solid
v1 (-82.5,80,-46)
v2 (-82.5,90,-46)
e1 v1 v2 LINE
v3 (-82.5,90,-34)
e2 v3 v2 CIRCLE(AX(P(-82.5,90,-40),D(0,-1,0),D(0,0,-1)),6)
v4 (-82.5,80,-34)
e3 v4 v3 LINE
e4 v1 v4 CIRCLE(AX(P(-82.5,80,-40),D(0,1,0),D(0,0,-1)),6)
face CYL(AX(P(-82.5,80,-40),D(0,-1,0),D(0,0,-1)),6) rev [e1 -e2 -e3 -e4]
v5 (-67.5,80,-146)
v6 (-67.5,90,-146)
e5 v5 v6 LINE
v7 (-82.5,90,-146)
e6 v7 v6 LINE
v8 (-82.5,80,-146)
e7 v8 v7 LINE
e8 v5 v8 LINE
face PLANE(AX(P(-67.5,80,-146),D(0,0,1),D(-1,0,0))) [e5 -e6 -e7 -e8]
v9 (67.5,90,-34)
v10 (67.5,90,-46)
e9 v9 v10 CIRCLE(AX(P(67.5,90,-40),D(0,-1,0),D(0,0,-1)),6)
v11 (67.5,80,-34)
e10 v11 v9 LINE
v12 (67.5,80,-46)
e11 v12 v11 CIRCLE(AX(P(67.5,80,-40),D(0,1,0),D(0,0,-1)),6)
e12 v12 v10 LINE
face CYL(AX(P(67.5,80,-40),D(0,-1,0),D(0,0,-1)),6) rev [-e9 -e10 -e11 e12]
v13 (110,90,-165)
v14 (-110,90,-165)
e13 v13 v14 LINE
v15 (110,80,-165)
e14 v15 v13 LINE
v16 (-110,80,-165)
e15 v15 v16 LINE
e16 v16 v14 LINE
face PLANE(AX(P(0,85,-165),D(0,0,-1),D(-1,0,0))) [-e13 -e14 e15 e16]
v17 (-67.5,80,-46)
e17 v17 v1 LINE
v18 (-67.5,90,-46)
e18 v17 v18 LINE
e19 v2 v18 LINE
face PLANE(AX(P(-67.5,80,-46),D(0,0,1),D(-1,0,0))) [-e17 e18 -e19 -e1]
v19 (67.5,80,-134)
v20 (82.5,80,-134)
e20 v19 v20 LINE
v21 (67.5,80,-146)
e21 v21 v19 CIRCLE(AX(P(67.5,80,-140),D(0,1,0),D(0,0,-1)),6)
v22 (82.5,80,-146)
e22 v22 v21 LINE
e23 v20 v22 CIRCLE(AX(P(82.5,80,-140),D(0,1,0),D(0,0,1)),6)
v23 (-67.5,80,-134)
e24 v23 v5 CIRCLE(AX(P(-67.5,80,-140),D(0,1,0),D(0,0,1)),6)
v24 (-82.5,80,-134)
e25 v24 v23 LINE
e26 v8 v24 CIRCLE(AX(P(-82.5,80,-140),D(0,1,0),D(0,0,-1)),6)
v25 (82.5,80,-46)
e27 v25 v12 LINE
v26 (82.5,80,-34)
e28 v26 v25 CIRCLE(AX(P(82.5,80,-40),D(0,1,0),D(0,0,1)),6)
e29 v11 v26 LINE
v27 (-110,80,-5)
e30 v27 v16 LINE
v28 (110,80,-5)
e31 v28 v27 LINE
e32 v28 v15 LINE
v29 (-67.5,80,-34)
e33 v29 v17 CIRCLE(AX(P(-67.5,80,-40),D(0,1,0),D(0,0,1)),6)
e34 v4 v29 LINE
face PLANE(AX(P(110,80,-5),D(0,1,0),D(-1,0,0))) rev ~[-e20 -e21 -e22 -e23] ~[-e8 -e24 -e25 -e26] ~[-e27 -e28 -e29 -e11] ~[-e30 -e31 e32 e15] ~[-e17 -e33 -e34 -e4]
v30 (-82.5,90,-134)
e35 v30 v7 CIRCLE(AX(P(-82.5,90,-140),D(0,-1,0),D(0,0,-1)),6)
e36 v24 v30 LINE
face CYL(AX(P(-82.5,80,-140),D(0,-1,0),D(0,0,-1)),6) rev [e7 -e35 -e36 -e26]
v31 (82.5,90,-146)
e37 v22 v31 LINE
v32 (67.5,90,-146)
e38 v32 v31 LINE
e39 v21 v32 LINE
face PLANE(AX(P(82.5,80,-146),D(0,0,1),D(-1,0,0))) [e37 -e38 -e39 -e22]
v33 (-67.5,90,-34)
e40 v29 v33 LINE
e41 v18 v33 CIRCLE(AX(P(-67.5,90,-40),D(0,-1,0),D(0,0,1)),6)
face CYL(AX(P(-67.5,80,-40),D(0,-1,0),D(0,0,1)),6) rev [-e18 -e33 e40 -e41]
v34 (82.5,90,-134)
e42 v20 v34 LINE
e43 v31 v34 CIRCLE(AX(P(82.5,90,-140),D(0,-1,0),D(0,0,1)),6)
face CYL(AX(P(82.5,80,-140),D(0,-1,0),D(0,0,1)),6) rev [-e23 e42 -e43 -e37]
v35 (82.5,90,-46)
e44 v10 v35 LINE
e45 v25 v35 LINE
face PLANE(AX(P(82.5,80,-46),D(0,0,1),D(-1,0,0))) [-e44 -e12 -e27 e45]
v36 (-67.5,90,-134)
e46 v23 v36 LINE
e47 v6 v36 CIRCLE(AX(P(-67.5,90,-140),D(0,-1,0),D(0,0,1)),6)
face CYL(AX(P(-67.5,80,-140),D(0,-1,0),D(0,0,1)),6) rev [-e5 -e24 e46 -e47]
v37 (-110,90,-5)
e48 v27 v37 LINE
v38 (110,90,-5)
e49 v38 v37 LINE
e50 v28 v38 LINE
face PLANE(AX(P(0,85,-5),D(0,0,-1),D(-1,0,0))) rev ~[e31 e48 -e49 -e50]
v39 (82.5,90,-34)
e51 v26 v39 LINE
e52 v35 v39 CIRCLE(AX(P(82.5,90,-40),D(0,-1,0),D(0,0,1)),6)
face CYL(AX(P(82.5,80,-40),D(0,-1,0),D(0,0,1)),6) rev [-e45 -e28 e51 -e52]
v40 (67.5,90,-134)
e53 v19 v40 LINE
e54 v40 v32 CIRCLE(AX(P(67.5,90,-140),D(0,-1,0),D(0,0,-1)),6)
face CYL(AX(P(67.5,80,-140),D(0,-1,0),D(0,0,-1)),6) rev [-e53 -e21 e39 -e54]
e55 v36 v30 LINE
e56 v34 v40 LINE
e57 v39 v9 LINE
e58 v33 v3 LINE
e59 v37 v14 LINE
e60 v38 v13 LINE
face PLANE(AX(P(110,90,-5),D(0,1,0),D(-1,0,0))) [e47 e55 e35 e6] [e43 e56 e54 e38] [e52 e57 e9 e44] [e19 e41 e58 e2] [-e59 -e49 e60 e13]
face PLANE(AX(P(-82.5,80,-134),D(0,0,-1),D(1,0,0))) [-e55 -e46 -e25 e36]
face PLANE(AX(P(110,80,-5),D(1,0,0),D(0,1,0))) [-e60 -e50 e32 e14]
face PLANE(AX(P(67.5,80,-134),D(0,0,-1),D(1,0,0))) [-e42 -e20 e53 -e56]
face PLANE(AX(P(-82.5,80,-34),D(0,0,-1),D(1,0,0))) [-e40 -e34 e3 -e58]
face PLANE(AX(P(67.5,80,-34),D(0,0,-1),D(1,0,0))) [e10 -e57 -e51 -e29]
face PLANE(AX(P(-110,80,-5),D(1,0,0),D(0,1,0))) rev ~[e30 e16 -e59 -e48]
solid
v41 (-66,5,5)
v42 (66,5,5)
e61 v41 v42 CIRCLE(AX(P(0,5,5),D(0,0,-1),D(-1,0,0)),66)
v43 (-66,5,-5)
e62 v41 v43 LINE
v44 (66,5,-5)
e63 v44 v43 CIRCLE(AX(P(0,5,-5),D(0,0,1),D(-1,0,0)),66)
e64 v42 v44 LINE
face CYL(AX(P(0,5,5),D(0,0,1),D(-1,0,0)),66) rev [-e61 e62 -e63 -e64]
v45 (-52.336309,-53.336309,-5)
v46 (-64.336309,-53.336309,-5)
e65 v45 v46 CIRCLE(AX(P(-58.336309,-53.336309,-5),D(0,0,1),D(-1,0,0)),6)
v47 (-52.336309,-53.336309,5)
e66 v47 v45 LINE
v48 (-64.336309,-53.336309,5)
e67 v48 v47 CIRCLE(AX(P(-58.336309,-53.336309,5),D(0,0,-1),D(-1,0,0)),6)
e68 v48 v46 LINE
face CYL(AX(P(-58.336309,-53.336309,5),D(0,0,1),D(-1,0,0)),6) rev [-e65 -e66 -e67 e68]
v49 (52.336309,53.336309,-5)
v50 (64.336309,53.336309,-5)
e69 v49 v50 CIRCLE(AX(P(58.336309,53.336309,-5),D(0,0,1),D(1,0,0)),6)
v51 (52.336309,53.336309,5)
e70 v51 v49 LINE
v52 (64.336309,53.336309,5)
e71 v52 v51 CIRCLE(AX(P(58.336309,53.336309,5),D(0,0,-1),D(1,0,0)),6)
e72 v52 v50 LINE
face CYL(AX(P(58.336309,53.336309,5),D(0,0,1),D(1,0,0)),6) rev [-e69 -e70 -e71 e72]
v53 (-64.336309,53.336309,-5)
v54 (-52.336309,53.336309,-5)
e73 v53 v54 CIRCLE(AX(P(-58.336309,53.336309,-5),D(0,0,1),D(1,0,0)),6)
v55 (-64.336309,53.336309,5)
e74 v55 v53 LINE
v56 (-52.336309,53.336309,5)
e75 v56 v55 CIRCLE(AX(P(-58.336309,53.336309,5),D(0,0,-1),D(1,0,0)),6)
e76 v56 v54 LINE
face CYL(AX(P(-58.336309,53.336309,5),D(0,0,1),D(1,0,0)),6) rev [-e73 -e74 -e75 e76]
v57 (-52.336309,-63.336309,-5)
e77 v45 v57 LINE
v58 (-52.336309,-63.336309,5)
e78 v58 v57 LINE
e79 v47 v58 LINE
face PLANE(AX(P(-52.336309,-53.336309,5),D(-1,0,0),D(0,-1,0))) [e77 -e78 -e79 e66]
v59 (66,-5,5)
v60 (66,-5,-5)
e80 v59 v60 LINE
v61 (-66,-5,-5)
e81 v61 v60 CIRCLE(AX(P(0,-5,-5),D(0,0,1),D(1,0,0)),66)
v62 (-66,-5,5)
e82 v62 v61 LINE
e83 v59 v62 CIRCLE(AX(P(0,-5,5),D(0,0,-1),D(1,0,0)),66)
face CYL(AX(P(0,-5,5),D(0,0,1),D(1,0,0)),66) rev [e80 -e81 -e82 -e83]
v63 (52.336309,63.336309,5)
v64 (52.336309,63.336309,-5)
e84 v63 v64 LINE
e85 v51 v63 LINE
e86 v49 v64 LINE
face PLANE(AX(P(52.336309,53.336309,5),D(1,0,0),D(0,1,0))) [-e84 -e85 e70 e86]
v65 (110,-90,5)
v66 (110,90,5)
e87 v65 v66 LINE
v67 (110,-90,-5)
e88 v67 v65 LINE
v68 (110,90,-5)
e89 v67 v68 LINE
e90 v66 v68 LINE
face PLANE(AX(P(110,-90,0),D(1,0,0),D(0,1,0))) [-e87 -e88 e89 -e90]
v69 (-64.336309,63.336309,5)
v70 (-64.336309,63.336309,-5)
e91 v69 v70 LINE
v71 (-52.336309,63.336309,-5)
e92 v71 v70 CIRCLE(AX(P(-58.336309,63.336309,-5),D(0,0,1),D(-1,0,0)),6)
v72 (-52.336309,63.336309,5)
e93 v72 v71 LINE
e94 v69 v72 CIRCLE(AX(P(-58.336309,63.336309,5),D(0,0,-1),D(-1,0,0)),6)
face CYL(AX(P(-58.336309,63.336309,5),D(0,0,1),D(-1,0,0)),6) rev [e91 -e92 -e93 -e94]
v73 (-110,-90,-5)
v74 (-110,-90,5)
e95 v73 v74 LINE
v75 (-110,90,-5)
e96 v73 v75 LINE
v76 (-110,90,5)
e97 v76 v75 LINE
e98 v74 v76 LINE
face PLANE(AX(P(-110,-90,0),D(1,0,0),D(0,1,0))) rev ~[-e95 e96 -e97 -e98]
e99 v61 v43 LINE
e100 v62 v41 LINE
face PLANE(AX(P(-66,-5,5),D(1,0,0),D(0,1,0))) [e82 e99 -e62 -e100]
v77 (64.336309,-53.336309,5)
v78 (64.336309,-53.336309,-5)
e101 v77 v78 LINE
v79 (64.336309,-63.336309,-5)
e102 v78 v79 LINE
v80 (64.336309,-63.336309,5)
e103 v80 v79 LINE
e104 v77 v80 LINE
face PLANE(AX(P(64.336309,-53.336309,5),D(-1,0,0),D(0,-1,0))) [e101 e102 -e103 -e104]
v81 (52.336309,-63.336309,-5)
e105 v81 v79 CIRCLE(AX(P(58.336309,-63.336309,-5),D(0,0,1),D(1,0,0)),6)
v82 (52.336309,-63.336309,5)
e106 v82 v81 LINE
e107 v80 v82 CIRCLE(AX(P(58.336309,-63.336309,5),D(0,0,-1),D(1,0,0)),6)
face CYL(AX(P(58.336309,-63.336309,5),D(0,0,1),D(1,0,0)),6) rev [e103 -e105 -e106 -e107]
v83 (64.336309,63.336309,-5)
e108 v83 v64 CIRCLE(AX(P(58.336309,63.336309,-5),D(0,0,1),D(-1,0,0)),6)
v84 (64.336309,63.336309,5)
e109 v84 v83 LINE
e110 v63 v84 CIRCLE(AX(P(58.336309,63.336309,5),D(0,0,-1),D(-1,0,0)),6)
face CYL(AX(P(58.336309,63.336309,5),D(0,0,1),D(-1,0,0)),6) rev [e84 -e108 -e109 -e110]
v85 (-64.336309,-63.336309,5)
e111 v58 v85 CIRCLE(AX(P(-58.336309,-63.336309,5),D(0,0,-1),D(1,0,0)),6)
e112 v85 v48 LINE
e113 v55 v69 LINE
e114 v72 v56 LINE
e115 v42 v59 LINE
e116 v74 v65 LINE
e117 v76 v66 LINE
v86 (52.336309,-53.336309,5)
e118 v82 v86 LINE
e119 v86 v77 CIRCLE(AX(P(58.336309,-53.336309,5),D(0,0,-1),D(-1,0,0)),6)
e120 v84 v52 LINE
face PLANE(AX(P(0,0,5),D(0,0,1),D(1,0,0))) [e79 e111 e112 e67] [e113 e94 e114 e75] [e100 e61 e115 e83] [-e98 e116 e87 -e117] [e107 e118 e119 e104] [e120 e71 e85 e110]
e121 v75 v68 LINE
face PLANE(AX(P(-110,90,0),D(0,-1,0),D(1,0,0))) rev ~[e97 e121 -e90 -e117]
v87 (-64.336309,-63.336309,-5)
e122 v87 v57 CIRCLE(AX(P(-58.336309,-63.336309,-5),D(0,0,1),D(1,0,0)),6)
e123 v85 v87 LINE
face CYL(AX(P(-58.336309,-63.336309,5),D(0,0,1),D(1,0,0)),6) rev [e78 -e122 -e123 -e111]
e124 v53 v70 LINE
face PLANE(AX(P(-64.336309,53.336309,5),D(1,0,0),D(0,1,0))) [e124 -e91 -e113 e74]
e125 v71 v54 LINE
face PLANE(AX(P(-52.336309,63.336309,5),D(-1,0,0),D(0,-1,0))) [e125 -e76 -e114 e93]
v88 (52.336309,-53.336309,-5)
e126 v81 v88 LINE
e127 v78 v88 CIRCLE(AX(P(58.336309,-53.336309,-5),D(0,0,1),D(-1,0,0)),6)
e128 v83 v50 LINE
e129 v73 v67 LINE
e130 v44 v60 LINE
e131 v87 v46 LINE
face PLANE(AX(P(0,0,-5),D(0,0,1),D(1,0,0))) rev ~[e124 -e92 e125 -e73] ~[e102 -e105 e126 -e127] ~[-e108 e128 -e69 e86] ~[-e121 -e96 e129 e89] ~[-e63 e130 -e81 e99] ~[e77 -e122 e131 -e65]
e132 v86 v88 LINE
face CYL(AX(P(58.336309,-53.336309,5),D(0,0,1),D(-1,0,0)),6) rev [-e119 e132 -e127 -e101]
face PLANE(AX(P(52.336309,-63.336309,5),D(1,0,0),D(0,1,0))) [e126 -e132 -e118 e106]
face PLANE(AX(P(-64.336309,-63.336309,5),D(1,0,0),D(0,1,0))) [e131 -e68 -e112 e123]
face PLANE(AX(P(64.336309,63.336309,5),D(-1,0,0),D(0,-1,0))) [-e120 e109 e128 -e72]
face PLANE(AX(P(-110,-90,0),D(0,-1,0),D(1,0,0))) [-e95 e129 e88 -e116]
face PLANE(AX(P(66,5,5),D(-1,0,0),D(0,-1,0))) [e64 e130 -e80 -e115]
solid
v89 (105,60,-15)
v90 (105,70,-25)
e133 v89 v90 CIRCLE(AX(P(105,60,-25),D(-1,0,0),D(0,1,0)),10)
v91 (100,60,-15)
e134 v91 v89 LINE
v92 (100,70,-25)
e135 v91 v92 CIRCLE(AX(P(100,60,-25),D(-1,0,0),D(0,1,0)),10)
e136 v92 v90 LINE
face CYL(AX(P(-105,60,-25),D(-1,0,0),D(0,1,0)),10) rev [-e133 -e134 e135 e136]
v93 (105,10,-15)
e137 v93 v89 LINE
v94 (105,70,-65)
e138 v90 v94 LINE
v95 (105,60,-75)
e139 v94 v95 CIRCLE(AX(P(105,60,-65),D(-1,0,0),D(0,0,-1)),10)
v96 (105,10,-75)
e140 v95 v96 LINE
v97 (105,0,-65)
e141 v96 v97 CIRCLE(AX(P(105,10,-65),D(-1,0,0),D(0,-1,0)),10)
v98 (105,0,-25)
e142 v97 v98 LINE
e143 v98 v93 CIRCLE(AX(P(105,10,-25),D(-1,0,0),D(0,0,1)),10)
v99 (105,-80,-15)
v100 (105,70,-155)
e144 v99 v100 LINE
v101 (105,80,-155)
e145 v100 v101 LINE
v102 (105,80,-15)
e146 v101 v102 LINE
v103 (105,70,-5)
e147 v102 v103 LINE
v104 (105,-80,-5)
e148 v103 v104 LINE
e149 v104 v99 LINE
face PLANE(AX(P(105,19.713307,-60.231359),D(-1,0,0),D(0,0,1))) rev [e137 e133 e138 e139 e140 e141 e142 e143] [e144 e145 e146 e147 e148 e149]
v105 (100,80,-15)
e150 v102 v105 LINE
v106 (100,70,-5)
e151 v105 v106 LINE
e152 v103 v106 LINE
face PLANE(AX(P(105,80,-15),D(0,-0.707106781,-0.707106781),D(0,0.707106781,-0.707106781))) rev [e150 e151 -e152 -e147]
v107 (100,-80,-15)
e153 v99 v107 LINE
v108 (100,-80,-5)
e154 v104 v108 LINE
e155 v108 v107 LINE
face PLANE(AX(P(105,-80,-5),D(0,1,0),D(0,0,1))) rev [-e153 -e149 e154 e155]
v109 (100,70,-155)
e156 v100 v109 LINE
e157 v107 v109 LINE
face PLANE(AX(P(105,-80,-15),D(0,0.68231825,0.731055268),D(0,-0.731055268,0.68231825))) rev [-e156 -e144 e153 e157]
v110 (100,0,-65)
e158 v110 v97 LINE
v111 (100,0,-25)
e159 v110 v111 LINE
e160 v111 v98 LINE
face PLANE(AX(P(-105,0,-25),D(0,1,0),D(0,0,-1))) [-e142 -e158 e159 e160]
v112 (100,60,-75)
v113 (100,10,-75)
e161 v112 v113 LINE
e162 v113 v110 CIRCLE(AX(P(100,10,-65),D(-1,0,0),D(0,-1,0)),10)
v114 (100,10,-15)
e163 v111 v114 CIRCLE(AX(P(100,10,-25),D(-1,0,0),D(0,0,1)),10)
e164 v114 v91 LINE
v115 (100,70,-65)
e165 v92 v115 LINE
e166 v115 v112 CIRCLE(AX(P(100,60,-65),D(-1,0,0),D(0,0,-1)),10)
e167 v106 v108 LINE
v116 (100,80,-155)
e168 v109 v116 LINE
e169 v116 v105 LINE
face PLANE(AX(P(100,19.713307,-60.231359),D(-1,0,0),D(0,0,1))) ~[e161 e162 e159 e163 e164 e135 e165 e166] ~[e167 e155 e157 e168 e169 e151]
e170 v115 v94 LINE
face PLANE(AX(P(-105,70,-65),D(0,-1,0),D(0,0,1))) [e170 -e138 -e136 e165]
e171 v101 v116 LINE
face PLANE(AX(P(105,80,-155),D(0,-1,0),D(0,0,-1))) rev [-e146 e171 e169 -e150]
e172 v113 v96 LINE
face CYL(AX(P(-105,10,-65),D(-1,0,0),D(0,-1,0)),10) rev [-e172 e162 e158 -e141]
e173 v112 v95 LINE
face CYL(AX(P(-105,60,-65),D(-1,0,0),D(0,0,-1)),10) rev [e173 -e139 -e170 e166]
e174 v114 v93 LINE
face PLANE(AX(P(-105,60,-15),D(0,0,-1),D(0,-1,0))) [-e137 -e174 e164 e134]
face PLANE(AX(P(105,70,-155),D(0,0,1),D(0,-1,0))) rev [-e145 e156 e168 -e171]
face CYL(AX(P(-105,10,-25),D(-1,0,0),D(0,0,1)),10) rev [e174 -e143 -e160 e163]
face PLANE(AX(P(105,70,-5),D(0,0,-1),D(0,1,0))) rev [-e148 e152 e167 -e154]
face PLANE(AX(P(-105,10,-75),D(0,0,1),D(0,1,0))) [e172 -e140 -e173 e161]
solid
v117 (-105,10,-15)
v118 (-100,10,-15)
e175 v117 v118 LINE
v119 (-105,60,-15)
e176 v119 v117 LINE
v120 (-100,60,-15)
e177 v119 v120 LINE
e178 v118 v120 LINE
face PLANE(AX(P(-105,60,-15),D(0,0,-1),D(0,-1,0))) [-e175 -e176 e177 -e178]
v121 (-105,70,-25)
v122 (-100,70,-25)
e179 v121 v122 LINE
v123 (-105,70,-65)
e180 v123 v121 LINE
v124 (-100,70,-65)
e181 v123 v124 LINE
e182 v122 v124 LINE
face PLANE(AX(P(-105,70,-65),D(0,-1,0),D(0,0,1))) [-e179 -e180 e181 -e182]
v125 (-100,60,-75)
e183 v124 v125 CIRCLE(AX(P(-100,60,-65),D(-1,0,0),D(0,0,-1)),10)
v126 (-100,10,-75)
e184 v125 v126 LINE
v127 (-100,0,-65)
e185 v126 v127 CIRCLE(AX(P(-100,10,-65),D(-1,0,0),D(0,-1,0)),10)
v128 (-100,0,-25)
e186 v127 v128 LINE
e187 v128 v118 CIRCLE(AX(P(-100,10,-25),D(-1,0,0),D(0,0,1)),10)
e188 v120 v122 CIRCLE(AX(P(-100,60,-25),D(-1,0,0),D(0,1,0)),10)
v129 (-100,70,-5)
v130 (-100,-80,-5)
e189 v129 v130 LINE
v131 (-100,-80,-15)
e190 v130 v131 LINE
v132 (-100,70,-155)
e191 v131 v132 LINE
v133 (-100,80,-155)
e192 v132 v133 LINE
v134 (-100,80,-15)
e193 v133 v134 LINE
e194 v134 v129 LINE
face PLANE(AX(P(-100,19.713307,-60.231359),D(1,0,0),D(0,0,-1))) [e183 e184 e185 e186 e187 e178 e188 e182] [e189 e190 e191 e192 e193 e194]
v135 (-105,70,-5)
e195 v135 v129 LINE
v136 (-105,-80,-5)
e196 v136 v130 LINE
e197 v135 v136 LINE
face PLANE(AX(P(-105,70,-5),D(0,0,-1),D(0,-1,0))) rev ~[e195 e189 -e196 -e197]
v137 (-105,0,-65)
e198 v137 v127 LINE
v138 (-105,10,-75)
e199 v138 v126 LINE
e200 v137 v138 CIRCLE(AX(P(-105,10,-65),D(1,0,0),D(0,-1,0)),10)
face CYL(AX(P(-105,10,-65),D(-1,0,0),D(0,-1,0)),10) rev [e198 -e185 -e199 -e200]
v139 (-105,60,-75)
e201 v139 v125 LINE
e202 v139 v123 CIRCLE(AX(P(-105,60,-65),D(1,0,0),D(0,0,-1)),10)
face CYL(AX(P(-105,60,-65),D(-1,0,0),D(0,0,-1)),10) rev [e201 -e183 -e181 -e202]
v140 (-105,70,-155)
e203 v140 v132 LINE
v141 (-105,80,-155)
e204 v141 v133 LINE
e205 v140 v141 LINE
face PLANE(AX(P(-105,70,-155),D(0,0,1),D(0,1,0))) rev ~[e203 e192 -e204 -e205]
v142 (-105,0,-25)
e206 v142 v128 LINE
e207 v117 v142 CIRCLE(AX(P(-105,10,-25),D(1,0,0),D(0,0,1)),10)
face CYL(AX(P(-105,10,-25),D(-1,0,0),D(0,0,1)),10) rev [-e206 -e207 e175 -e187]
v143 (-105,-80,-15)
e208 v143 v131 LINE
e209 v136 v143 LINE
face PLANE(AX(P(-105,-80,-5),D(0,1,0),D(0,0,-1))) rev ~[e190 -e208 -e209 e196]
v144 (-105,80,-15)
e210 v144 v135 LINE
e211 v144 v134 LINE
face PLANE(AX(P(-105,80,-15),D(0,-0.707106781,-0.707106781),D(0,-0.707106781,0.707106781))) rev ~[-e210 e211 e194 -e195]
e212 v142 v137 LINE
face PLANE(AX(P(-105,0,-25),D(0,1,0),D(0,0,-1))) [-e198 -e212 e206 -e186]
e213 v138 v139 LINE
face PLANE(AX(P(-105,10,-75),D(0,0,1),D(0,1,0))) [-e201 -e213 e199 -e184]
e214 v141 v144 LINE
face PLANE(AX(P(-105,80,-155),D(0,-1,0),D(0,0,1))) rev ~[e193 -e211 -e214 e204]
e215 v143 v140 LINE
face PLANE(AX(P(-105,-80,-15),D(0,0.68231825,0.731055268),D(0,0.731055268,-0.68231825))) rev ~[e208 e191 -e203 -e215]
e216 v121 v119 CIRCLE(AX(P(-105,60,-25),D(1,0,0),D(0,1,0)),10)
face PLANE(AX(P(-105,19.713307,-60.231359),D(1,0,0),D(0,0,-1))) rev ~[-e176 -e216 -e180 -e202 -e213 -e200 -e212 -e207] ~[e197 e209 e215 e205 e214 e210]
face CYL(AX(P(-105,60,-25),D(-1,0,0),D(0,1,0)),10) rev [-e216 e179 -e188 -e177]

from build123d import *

# Parameters (mm, degrees)
SKETCH1_W            = 220
SKETCH1_H            = 180
BOSS_EXTRUDE1_DEPTH  = 5
SKETCH2_R            = 65.5
CUT_EXTRUDE1_DEPTH   = 55
SKETCH3_R            = 5.5
CUT_EXTRUDE2_DEPTH   = 55
CIRPATTERN1_COUNT    = 4
SKETCH4_W            = 220
SKETCH4_H            = 10
BOSS_EXTRUDE2_DEPTH  = 160
BOSS_EXTRUDE3_START  = -5
BOSS_EXTRUDE3_DEPTH  = 5
CUT_EXTRUDE3_DEPTH   = 15
CUT_EXTRUDE4_DEPTH   = 16
CUT_EXTRUDE5_DEPTH   = 16
LPATTERN1_COUNT      = 2
LPATTERN1_PITCH      = 150
LPATTERN1_COUNT_DIR2 = 2
LPATTERN1_PITCH_DIR2 = 100
CUT_EXTRUDE6_DEPTH   = 317


with BuildPart() as part:
    # Sketch1 → Boss-Extrude1 (new, symmetric)
    with BuildSketch(Plane.XY):
        Rectangle(SKETCH1_W, SKETCH1_H)
    extrude(amount=BOSS_EXTRUDE1_DEPTH, both=True)

    # Sketch2 → Cut-Extrude1 (cut)
    with BuildSketch(Plane(origin=(0, 0, -5), x_dir=(-1, 0, 0), z_dir=(0, 0, -1))):
        Circle(SKETCH2_R)
    extrude(amount=-CUT_EXTRUDE1_DEPTH, mode=Mode.SUBTRACT)

    # Sketch3 → Cut-Extrude2 (cut)
    with BuildSketch(Plane(origin=(0, 0, -5), x_dir=(-1, 0, 0), z_dir=(0, 0, -1))):
        with Locations((-58.336309448, 58.336309448)):
            Circle(SKETCH3_R)
    cut_extrude2 = extrude(amount=-CUT_EXTRUDE2_DEPTH, mode=Mode.SUBTRACT)

    # CirPattern1: Cut-Extrude2 ×4 about axis
    cirpattern1_axis = Axis((0, 0, 0), (0, 0, 1))
    for i in range(1, CIRPATTERN1_COUNT):
        add(cut_extrude2.rotate(cirpattern1_axis, i * 360 / CIRPATTERN1_COUNT), mode=Mode.SUBTRACT)

    # Sketch7 → Cut-Extrude3 (cut)
    with BuildSketch(Plane.XY.offset(5)):
        with BuildLine():
            Line((-52.336309448, 63.336309448), (-52.336309448, 53.336309448))
            ThreePointArc((-52.336309448, 53.336309448), (-58.336309448, 47.336309448), (-64.336309448, 53.336309448))
            Line((-64.336309448, 53.336309448), (-64.336309448, 63.336309448))
            ThreePointArc((-64.336309448, 63.336309448), (-58.336309448, 69.336309448), (-52.336309448, 63.336309448))
        make_face()
        with BuildLine():
            Line((64.336309448, 63.336309448), (64.336309448, 53.336309448))
            ThreePointArc((64.336309448, 53.336309448), (58.336309448, 47.336309448), (52.336309448, 53.336309448))
            Line((52.336309448, 53.336309448), (52.336309448, 63.336309448))
            ThreePointArc((52.336309448, 63.336309448), (58.336309448, 69.336309448), (64.336309448, 63.336309448))
        make_face()
        with BuildLine():
            Line((52.336309448, -63.336309448), (52.336309448, -53.336309448))
            ThreePointArc((52.336309448, -53.336309448), (58.336309448, -47.336309448), (64.336309448, -53.336309448))
            Line((64.336309448, -53.336309448), (64.336309448, -63.336309448))
            ThreePointArc((64.336309448, -63.336309448), (58.336309448, -69.336309448), (52.336309448, -63.336309448))
        make_face()
        with BuildLine():
            Line((-52.336309448, -53.336309448), (-52.336309448, -63.336309448))
            ThreePointArc((-52.336309448, -63.336309448), (-58.336309448, -69.336309448), (-64.336309448, -63.336309448))
            Line((-64.336309448, -63.336309448), (-64.336309448, -53.336309448))
            ThreePointArc((-64.336309448, -53.336309448), (-58.336309448, -47.336309448), (-52.336309448, -53.336309448))
        make_face()
    extrude(amount=-CUT_EXTRUDE3_DEPTH, mode=Mode.SUBTRACT)

    # Sketch8 → Cut-Extrude4 (cut)
    with BuildSketch(Plane.XY.offset(5)):
        with BuildLine():
            Line((66, 5), (66, -5))
            ThreePointArc((66, -5), (0, -71), (-66, -5))
            Line((-66, -5), (-66, 5))
            ThreePointArc((-66, 5), (0, 71), (66, 5))
        make_face()
    extrude(amount=-CUT_EXTRUDE4_DEPTH, mode=Mode.SUBTRACT)


with BuildPart() as body_2:
    # Sketch4 → Boss-Extrude2 (new body)
    with BuildSketch(Plane(origin=(0, 0, -5), x_dir=(-1, 0, 0), z_dir=(0, 0, -1))):
        with Locations((0, 85)):
            Rectangle(SKETCH4_W, SKETCH4_H)
    extrude(amount=BOSS_EXTRUDE2_DEPTH)

    # Sketch9 → Cut-Extrude5 (cut)
    with BuildSketch(Plane.XZ.offset(-80)):
        with BuildLine():
            Line((67.5, -34), (82.5, -34))
            ThreePointArc((82.5, -34), (88.5, -40), (82.5, -46))
            Line((82.5, -46), (67.5, -46))
            ThreePointArc((67.5, -46), (61.5, -40), (67.5, -34))
        make_face()
    cut_extrude5 = extrude(amount=-CUT_EXTRUDE5_DEPTH, mode=Mode.SUBTRACT)

    # LPattern1: Cut-Extrude5 2 × 2
    with Locations(*[(-i * LPATTERN1_PITCH, 0, -j * LPATTERN1_PITCH_DIR2) for i in range(LPATTERN1_COUNT) for j in range(LPATTERN1_COUNT_DIR2) if (i, j) != (0, 0)]):
        add(cut_extrude5, mode=Mode.SUBTRACT)


with BuildPart() as body_3:
    # Sketch6 → Boss-Extrude3 (new body)
    with BuildSketch(Plane.ZY.offset(110).offset(BOSS_EXTRUDE3_START)):
        Polygon((-5, 70), (-5, -80), (-15, -80), (-155, 70), (-155, 80), (-15, 80), align=None)
    extrude(amount=-BOSS_EXTRUDE3_DEPTH)


with BuildPart() as body_4:
    # Mirror1: mirrored copy
    add(body_3.part.mirror(Plane(origin=(0, 0, 0), x_dir=(0, 0, 1), z_dir=(1, 0, 0))))


with BuildPart() as cut_extrude6_tool:
    # Sketch10 → Cut-Extrude6 (new body)
    with BuildSketch(Plane.ZY.offset(105)):
        with BuildLine():
            Line((-65, 70), (-25, 70))
            ThreePointArc((-25, 70), (-17.928932188, 67.071067812), (-15, 60))
            Line((-15, 60), (-15, 10))
            ThreePointArc((-15, 10), (-17.928932188, 2.928932188), (-25, 0))
            Line((-25, 0), (-65, 0))
            ThreePointArc((-65, 0), (-72.071067812, 2.928932188), (-75, 10))
            Line((-75, 10), (-75, 60))
            ThreePointArc((-75, 60), (-72.071067812, 67.071067812), (-65, 70))
        make_face()
    extrude(amount=-CUT_EXTRUDE6_DEPTH)


with BuildPart() as body_3_1:
    add(body_3.part)

    # Cut-Extrude6: cut by cut_extrude6_tool
    add(cut_extrude6_tool.part, mode=Mode.SUBTRACT)


with BuildPart() as body_4_1:
    add(body_4.part)

    # Cut-Extrude6: cut by cut_extrude6_tool
    add(cut_extrude6_tool.part, mode=Mode.SUBTRACT)


solid = Compound([part.part, body_2.part, body_3_1.part, body_4_1.part])
